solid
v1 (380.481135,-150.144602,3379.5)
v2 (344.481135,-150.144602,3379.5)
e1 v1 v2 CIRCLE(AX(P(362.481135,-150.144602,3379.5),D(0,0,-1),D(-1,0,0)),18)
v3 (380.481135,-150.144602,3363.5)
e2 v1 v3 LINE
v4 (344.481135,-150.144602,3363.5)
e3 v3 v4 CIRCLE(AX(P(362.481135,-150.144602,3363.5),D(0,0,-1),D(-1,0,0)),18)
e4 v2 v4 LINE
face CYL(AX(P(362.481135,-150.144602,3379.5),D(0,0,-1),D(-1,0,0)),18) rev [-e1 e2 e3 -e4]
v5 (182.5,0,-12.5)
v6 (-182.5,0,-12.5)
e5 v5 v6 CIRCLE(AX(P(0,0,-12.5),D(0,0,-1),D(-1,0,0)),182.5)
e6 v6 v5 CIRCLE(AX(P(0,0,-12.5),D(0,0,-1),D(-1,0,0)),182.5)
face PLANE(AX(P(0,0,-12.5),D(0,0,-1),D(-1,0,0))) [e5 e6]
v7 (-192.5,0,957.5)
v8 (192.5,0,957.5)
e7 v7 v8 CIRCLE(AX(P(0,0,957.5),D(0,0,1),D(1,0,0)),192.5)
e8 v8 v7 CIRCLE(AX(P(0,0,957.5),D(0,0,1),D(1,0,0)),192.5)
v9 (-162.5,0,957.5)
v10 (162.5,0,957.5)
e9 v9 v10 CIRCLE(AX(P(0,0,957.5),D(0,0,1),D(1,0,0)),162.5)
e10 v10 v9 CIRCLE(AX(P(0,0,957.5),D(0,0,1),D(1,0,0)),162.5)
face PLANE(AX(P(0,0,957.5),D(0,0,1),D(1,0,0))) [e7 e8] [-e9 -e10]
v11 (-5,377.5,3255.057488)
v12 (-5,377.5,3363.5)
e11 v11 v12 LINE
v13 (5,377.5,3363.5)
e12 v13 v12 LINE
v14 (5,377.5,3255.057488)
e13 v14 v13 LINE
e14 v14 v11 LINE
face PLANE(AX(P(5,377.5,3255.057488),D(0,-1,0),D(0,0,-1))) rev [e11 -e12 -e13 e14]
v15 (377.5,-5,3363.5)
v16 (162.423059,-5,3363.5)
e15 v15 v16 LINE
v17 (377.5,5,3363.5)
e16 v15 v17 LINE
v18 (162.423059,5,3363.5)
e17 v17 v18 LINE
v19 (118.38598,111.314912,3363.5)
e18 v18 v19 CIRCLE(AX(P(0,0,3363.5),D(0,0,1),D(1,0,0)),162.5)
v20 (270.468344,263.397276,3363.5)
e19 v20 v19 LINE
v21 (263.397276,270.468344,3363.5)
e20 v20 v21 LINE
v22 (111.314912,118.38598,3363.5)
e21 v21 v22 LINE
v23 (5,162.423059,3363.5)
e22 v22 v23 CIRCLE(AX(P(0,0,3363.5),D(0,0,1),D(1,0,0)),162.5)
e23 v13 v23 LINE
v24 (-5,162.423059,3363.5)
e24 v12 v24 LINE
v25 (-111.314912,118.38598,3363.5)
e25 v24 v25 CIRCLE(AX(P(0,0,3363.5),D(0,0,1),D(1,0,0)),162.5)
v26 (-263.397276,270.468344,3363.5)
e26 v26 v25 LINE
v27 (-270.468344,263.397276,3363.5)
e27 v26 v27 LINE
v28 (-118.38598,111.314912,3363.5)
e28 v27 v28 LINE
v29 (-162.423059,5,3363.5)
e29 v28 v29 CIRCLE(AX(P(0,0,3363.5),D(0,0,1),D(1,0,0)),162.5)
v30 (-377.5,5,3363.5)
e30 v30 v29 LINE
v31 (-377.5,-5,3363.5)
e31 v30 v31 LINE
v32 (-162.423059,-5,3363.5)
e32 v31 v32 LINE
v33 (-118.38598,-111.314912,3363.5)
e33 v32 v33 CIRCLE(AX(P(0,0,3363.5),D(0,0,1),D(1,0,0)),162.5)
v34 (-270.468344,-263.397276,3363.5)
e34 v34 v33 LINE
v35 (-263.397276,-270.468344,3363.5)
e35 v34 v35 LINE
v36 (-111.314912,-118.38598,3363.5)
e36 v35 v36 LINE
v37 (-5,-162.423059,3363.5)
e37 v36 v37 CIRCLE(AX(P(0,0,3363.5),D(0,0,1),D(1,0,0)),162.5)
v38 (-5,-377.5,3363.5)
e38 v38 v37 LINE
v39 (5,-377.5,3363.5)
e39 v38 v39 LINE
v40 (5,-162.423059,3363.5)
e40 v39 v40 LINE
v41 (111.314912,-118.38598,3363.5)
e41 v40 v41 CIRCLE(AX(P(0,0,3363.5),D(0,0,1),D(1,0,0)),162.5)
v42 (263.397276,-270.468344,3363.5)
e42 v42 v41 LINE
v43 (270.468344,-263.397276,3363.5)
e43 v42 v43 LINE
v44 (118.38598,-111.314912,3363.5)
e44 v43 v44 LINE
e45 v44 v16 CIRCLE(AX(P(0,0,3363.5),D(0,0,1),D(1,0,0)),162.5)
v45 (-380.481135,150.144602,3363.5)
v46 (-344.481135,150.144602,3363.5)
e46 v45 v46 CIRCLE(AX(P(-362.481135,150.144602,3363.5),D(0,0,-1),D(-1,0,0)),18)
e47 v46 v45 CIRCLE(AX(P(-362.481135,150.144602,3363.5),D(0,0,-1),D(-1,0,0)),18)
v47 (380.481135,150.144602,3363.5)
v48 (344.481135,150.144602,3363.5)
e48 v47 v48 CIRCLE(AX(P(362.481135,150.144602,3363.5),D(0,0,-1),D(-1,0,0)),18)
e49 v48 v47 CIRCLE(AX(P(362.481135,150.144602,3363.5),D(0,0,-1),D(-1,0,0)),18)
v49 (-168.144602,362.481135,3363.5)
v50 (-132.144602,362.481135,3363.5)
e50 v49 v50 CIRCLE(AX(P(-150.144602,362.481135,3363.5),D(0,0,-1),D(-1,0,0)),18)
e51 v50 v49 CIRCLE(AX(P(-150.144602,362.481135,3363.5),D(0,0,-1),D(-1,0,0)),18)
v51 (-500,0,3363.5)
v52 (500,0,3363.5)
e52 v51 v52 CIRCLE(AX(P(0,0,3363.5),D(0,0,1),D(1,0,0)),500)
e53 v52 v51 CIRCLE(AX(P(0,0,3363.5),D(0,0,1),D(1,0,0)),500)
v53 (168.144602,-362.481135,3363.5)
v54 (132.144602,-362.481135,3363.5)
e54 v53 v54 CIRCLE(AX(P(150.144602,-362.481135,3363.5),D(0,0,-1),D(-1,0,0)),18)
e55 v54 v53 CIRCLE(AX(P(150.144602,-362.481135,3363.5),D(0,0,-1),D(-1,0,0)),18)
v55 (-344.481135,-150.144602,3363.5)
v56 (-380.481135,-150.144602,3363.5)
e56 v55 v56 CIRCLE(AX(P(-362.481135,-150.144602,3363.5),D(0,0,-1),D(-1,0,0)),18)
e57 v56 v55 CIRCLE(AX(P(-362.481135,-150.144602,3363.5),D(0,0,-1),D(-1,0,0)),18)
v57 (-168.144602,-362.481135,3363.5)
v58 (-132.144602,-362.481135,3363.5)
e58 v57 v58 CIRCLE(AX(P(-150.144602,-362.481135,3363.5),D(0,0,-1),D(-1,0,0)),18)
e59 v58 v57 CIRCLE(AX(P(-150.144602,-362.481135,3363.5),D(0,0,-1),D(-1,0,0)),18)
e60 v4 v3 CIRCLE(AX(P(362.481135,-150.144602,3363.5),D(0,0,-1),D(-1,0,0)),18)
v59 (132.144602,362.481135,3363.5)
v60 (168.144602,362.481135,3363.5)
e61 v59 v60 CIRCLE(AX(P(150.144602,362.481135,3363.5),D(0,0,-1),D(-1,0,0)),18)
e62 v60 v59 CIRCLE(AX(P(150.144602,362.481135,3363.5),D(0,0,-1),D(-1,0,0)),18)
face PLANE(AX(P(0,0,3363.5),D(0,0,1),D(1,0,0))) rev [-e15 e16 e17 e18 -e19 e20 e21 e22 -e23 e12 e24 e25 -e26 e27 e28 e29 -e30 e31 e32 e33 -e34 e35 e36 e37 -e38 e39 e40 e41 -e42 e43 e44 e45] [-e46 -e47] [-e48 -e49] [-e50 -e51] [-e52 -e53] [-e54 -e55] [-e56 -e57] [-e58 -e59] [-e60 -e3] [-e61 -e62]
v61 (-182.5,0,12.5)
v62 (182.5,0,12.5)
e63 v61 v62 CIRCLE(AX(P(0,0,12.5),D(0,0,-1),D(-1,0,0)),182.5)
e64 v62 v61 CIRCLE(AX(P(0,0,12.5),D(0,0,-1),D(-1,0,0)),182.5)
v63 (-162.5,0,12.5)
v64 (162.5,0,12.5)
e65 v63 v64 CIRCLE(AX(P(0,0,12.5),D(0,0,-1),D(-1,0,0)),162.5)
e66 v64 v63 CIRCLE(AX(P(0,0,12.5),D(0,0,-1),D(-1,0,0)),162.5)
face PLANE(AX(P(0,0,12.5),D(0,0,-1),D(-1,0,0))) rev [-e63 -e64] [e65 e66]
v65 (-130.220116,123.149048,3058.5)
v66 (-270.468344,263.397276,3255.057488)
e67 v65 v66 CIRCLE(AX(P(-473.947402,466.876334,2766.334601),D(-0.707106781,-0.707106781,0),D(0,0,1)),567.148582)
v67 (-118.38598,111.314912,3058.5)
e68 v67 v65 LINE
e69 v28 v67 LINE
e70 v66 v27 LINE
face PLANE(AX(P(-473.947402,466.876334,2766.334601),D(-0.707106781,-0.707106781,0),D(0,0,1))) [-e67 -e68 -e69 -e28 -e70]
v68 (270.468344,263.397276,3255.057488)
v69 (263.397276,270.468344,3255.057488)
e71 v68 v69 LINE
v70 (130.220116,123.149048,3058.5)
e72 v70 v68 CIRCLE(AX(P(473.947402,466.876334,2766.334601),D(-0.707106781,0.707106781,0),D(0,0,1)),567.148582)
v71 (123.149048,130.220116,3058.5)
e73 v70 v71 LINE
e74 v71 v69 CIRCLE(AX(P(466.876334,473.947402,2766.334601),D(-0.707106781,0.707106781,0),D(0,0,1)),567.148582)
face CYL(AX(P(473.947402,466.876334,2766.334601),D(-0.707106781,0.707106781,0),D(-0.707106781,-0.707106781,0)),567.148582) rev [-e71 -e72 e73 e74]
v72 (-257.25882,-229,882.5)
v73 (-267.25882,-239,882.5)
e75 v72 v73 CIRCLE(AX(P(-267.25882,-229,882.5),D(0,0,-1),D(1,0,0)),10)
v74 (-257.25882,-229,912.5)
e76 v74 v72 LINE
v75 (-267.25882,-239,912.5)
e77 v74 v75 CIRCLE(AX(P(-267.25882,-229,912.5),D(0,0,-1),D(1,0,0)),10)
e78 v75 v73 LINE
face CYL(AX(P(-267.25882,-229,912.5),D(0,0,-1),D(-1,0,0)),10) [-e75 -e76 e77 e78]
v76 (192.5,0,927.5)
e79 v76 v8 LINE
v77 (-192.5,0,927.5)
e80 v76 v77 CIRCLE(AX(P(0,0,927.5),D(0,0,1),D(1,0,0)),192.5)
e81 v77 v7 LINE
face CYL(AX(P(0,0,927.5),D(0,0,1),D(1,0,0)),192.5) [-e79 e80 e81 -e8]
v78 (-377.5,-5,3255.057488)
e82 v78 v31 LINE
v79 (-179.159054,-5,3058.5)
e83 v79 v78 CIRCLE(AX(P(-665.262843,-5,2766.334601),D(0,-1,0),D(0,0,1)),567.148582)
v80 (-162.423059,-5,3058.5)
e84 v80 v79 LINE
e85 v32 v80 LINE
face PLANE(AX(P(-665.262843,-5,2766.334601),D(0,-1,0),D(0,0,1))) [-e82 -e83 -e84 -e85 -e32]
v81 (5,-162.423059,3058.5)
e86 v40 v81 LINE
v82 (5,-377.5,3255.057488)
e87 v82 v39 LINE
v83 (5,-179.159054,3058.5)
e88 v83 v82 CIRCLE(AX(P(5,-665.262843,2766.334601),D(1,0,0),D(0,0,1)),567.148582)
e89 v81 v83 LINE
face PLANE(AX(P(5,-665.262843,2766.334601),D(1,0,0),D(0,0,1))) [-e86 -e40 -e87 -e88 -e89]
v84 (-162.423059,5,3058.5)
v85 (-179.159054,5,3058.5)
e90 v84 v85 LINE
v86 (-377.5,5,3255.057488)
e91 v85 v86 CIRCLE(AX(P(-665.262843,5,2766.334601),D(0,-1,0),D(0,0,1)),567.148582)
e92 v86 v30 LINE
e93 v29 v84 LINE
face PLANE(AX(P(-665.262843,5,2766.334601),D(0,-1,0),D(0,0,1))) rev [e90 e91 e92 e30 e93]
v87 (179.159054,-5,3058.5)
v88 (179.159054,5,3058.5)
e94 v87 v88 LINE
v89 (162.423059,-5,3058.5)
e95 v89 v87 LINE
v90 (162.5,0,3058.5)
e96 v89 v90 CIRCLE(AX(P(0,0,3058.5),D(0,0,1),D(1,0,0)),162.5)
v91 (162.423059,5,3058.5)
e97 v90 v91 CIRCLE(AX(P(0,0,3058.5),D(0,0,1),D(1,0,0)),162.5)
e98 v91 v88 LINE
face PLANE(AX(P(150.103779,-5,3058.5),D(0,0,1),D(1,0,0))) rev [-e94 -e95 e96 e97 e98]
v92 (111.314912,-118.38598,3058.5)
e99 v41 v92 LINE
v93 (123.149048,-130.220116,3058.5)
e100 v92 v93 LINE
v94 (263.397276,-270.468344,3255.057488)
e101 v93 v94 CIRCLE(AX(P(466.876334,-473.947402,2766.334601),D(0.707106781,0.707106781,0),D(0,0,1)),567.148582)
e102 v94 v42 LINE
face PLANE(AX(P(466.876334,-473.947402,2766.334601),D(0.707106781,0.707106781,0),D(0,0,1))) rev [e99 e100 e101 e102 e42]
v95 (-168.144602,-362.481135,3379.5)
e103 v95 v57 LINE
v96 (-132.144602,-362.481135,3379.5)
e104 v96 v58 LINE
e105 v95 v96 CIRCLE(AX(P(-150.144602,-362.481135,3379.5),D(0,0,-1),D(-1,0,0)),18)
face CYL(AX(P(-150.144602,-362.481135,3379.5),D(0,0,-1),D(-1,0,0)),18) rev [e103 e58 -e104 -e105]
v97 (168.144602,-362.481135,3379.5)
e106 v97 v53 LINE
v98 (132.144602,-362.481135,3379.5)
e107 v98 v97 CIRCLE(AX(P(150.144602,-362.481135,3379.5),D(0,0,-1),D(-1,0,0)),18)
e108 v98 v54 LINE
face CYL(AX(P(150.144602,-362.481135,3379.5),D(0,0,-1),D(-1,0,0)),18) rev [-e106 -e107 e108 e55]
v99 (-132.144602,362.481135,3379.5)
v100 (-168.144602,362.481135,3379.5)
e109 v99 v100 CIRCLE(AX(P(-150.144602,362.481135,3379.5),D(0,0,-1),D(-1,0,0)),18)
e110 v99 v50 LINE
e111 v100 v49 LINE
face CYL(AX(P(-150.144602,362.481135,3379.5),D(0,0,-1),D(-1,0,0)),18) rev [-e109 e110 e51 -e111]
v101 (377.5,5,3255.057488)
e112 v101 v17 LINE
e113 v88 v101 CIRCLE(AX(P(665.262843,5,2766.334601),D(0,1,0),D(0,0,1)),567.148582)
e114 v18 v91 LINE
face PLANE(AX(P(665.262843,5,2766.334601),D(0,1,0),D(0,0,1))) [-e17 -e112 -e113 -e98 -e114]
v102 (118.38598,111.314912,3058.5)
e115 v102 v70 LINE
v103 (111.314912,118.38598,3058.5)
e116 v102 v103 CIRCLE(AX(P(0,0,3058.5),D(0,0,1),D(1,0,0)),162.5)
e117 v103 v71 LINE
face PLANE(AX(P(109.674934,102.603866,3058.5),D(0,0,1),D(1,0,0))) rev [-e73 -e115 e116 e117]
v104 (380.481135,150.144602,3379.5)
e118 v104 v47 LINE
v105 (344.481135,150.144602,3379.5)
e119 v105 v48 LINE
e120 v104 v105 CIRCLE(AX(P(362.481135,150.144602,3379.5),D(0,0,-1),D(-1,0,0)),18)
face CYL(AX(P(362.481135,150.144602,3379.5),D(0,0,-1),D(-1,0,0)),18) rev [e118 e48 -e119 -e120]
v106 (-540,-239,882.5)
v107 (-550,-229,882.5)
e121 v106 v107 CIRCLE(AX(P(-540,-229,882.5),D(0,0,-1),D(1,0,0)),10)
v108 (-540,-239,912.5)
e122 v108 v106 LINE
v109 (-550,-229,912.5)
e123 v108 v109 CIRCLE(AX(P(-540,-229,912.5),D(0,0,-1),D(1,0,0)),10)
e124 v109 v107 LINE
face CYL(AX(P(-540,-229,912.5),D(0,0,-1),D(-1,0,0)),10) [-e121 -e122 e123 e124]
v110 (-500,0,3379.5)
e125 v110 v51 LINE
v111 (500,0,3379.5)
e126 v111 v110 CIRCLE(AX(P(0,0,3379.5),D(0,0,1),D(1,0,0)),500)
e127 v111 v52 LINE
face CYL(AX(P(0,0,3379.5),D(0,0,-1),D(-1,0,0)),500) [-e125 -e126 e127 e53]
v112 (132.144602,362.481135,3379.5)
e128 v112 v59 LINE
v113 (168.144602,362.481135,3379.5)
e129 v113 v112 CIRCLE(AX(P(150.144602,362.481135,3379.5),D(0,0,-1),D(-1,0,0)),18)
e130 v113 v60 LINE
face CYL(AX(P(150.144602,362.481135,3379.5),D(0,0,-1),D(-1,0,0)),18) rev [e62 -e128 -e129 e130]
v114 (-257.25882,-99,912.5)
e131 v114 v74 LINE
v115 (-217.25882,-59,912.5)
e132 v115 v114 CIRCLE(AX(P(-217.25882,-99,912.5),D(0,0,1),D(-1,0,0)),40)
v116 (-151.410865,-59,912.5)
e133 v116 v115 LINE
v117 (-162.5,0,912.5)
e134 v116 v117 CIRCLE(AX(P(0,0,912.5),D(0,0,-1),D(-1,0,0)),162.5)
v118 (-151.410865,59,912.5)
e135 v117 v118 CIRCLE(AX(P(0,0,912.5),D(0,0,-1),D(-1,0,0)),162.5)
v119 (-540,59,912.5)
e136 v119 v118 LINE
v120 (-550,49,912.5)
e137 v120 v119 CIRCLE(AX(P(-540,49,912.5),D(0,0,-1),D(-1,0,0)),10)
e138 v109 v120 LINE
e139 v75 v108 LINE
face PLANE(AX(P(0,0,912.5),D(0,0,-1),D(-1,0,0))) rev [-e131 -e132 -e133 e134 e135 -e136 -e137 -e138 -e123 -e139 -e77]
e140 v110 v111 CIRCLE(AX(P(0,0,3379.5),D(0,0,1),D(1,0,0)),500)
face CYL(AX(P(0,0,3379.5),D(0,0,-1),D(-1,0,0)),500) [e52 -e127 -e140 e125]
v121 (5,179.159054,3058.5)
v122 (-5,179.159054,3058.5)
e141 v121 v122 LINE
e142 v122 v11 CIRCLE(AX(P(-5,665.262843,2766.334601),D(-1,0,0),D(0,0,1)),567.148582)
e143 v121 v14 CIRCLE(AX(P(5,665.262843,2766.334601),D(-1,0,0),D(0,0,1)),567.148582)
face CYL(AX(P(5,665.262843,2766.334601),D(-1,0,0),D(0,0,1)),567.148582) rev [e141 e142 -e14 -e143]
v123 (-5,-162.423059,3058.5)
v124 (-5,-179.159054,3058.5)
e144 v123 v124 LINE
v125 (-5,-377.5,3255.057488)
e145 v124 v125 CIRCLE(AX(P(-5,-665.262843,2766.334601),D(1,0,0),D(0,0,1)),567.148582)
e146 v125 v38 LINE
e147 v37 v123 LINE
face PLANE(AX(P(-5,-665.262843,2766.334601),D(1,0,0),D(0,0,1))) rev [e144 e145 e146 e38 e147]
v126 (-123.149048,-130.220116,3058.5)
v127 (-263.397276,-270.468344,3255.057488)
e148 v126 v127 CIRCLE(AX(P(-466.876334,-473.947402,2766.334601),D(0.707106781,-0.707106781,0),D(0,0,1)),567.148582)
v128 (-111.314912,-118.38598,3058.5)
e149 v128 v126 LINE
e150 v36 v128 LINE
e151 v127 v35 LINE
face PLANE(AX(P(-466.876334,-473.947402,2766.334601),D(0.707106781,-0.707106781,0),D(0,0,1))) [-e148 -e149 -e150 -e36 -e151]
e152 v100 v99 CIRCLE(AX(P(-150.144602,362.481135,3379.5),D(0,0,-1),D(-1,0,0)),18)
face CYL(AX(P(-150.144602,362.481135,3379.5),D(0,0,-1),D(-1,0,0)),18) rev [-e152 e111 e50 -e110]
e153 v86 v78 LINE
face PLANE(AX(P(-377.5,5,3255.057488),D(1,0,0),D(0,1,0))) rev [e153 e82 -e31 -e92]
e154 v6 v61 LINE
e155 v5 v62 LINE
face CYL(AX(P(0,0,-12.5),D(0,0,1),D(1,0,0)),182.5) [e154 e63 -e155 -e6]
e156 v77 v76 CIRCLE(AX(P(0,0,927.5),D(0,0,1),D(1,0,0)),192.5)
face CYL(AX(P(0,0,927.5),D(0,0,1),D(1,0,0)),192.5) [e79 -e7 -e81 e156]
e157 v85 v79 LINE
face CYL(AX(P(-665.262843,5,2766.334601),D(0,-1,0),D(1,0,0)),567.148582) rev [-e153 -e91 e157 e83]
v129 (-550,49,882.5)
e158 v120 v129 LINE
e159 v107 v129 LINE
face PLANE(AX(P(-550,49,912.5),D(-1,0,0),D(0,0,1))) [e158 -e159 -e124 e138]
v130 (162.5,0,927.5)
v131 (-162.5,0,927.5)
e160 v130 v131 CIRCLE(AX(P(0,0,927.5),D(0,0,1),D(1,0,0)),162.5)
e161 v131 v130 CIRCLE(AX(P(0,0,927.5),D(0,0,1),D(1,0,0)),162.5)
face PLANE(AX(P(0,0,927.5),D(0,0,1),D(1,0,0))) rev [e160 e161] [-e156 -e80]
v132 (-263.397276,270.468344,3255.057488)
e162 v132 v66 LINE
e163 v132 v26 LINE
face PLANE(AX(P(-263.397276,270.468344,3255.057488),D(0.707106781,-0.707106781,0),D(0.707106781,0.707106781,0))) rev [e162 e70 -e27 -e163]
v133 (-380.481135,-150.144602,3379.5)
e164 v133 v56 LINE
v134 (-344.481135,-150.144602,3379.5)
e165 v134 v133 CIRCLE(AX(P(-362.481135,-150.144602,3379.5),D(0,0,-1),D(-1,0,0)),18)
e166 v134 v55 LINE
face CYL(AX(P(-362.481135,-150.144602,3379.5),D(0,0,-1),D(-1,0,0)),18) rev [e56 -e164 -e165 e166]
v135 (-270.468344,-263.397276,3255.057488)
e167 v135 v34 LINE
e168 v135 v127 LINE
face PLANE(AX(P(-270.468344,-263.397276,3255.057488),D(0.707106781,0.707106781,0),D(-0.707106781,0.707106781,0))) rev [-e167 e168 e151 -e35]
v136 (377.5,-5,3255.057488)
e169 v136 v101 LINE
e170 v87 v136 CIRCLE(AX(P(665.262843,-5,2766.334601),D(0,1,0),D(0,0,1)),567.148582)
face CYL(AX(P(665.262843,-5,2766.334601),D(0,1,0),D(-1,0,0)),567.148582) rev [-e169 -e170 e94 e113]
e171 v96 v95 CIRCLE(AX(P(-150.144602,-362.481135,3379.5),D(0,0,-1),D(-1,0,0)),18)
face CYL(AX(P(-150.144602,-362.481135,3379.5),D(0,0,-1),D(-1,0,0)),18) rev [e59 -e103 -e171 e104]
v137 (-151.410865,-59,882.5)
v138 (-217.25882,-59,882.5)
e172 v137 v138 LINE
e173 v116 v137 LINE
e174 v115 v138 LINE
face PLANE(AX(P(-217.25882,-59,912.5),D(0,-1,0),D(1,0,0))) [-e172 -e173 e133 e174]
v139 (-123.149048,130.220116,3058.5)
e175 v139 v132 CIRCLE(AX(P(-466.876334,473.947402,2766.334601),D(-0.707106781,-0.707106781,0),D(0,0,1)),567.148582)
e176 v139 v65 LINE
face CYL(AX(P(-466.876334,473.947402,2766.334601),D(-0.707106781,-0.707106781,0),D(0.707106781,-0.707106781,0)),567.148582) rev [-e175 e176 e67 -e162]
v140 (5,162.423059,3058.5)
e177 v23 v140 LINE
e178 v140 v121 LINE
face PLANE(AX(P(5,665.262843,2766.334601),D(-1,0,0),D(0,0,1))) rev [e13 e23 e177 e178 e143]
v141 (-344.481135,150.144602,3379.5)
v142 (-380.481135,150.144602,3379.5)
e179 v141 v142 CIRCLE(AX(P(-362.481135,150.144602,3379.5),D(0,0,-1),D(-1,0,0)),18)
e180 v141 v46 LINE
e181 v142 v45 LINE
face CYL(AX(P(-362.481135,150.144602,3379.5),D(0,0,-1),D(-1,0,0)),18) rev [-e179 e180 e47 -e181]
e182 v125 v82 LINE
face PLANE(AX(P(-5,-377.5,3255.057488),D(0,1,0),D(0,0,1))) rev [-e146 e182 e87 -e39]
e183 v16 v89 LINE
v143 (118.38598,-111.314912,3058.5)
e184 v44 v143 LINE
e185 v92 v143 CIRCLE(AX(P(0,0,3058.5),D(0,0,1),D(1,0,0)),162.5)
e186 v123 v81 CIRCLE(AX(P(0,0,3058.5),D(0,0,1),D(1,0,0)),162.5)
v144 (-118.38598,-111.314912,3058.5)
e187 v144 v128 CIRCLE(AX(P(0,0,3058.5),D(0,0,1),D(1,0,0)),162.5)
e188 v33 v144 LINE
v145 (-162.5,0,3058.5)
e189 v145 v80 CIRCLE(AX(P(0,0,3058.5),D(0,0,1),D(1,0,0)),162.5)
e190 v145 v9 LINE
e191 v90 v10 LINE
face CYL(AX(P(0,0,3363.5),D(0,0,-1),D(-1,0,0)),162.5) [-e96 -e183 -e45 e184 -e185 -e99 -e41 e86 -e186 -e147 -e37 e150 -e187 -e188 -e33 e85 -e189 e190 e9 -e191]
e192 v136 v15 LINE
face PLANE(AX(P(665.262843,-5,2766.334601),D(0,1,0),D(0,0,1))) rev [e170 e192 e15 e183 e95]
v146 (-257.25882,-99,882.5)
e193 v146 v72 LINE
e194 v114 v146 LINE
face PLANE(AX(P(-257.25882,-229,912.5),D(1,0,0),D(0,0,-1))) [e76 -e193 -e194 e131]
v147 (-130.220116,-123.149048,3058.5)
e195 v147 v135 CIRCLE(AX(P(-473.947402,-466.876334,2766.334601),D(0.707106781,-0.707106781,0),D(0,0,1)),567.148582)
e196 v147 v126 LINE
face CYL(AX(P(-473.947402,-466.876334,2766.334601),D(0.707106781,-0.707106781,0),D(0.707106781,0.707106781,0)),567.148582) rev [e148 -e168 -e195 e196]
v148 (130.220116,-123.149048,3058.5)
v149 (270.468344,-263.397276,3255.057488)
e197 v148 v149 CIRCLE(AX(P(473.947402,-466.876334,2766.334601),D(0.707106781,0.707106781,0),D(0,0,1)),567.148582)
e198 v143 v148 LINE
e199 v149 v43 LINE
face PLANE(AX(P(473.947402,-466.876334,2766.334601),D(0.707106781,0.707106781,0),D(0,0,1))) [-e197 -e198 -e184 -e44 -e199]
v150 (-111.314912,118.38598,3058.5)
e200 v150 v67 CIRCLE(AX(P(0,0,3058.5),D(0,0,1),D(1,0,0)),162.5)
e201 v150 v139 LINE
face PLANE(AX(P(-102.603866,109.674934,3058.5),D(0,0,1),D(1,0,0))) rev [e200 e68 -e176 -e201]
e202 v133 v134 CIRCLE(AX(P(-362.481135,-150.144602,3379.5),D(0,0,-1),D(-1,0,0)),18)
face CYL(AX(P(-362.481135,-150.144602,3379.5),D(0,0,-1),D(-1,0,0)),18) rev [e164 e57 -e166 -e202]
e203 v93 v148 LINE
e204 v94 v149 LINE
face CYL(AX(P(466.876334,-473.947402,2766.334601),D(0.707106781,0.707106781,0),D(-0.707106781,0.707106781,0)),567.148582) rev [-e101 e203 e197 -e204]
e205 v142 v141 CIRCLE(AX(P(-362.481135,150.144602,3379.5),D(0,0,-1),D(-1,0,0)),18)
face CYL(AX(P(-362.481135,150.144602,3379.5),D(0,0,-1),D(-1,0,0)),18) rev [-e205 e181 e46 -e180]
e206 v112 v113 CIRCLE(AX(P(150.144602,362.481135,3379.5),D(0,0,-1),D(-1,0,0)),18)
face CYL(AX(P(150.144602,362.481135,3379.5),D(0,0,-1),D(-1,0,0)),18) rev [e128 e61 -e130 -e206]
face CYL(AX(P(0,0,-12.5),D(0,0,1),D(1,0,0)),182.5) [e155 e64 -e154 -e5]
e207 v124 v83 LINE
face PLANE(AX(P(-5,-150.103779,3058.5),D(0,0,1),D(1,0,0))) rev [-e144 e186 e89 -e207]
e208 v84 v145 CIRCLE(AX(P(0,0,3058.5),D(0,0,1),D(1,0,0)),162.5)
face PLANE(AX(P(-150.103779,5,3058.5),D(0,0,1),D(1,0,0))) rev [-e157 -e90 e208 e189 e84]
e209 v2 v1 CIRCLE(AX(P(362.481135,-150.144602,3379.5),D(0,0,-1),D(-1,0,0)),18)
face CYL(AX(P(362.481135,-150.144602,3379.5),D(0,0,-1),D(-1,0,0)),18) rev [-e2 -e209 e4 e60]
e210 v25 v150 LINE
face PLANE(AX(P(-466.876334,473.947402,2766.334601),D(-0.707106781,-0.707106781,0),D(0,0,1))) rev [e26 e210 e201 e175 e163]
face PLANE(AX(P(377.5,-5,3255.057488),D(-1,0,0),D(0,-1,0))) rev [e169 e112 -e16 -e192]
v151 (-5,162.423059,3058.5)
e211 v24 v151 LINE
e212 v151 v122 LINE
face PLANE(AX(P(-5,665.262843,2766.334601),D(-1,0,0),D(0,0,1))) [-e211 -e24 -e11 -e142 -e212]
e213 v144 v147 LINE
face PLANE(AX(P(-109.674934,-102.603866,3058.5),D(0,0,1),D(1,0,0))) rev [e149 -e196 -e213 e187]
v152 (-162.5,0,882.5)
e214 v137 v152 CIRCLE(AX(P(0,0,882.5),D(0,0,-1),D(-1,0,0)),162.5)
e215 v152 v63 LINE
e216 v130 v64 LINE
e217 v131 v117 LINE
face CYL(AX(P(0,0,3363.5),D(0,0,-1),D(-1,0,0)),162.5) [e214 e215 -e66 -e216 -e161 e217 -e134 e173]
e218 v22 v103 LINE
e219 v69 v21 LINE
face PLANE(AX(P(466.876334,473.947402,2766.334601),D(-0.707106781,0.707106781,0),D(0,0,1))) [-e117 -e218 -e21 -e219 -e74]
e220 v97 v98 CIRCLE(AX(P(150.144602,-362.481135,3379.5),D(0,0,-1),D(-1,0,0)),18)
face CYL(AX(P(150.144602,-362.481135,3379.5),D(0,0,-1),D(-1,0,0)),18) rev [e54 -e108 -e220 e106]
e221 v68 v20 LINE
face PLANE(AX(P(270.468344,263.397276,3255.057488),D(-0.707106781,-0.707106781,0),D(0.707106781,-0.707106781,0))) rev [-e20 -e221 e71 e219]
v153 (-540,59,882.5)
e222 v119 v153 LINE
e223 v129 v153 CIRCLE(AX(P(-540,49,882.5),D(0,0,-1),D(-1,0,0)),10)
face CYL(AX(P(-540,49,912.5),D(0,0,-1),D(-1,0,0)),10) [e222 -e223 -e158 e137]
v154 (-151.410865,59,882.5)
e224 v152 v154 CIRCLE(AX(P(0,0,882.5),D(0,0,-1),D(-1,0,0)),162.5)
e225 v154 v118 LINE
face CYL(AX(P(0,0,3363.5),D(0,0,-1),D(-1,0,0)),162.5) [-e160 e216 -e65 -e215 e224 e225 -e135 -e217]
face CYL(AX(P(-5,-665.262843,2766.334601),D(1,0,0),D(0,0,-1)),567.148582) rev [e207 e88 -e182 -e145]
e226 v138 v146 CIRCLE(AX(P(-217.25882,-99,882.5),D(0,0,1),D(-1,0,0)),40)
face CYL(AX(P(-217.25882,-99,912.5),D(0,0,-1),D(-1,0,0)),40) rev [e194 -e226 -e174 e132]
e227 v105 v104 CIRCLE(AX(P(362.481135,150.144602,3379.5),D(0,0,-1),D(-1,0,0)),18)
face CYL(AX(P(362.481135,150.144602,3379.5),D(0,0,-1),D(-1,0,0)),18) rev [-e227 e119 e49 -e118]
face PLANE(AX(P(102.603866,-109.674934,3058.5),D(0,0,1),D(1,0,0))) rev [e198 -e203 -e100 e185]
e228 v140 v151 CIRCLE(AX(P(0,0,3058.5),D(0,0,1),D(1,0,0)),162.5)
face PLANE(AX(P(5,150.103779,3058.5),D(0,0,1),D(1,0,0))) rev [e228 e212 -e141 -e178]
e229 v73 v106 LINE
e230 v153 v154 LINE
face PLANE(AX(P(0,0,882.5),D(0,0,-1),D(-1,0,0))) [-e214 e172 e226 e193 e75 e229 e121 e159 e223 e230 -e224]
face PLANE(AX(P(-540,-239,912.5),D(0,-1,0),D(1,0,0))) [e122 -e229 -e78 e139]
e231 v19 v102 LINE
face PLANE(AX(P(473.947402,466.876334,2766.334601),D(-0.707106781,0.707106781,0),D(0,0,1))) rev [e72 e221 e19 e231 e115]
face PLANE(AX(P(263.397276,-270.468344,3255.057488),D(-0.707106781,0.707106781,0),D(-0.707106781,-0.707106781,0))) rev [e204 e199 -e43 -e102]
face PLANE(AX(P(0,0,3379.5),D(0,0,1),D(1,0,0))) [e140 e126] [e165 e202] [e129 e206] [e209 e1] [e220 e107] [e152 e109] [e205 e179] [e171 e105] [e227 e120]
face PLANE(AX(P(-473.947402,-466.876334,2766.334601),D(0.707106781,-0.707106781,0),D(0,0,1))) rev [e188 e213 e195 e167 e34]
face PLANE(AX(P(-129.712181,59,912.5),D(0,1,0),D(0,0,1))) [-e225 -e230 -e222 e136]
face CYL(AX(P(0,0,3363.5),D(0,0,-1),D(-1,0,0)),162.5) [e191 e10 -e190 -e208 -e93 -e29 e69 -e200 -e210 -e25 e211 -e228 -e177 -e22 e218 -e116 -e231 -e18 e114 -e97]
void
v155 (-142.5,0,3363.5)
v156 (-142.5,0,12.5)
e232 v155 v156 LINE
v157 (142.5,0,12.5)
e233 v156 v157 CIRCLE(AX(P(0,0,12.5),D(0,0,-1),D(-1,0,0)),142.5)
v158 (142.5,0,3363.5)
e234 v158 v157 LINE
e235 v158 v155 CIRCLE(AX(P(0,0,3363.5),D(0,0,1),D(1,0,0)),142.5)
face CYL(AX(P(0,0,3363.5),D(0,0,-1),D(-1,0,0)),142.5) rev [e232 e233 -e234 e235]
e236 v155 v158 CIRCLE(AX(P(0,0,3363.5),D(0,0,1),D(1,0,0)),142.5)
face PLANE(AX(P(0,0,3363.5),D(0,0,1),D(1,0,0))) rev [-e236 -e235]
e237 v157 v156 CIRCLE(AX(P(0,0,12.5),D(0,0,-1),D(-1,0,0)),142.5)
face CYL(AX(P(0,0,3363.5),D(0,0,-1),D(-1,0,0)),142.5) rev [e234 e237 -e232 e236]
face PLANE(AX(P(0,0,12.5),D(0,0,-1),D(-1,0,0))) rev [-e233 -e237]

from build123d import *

# Parameters (mm, degrees)
SKETCH1_R           = 162.5
SKETCH1_R_2         = 142.5
BOSS_EXTRUDE1_DEPTH = 3363.5
BOSS_EXTRUDE2_START = -2436
SKETCH2_R           = 192.5
SKETCH2_R_2         = 162.5
BOSS_EXTRUDE2_DEPTH = 30
SKETCH3_R           = 500
BOSS_EXTRUDE3_DEPTH = 16
BOSS_EXTRUDE4_DEPTH = 5
CIRPATTERN1_COUNT   = 8
SKETCH5_R           = 18
CUT_EXTRUDE1_DEPTH  = 3438.023749
SKETCH6_R           = 182.5
BOSS_EXTRUDE5_DEPTH = 12.5
BOSS_EXTRUDE6_START = -895
BOSS_EXTRUDE6_DEPTH = 30


with BuildPart() as part:
    # Sketch1 → Boss-Extrude1 (new body)
    with BuildSketch(Plane.XY):
        Circle(SKETCH1_R)
        Circle(SKETCH1_R_2, mode=Mode.SUBTRACT)
    extrude(amount=BOSS_EXTRUDE1_DEPTH)

    # Sketch2 → Boss-Extrude2 (add)
    with BuildSketch(Plane.XY.offset(3363.5).offset(BOSS_EXTRUDE2_START)):
        Circle(SKETCH2_R)
        Circle(SKETCH2_R_2, mode=Mode.SUBTRACT)
    extrude(amount=BOSS_EXTRUDE2_DEPTH)

    # Sketch3 → Boss-Extrude3 (add)
    with BuildSketch(Plane.XY.offset(3363.5)):
        Circle(SKETCH3_R)
    extrude(amount=BOSS_EXTRUDE3_DEPTH)

    # Sketch4 → Boss-Extrude4 (add, symmetric)
    with BuildSketch(Plane(origin=(0, 0, 0), x_dir=(0, 0, -1), z_dir=(1, 0, 0))):
        with BuildLine():
            Line((-3058.5, 150.103779), (-3058.5, 179.159054))
            ThreePointArc((-3058.5, 179.159054), (-3169.176272, 266.043477), (-3255.057488, 377.5))
            Line((-3255.057488, 377.5), (-3363.5, 377.5))
            Line((-3363.5, 377.5), (-3363.5, 150.103779))
            Line((-3363.5, 150.103779), (-3058.5, 150.103779))
        make_face()
    boss_extrude4 = extrude(amount=BOSS_EXTRUDE4_DEPTH, both=True)

    # CirPattern1: Boss-Extrude4 ×8 about axis
    cirpattern1_axis = Axis((0, 0, 0), (0, 0, 1))
    for i in range(1, CIRPATTERN1_COUNT):
        add(boss_extrude4.rotate(cirpattern1_axis, i * 360 / CIRPATTERN1_COUNT))

    # Sketch5 → Cut-Extrude1 (cut, through all)
    with BuildSketch(Plane(origin=(0, 0, 3363.5), x_dir=(-1, 0, 0), z_dir=(0, 0, -1))):
        with Locations((150.144602, 362.481135)):
            Circle(SKETCH5_R)
        with Locations((362.481135, 150.144602)):
            Circle(SKETCH5_R)
        with Locations((362.481135, -150.144602)):
            Circle(SKETCH5_R)
        with Locations((150.144602, -362.481135)):
            Circle(SKETCH5_R)
        with Locations((-150.144602, -362.481135)):
            Circle(SKETCH5_R)
        with Locations((-362.481135, -150.144602)):
            Circle(SKETCH5_R)
        with Locations((-362.481135, 150.144602)):
            Circle(SKETCH5_R)
        with Locations((-150.144602, 362.481135)):
            Circle(SKETCH5_R)
    extrude(amount=-CUT_EXTRUDE1_DEPTH, mode=Mode.SUBTRACT)

    # Sketch6 → Boss-Extrude5 (add, symmetric)
    with BuildSketch(Plane(origin=(0, 0, 0), x_dir=(-1, 0, 0), z_dir=(0, 0, -1))):
        Circle(SKETCH6_R)
    extrude(amount=BOSS_EXTRUDE5_DEPTH, both=True)

    # Sketch7 → Boss-Extrude6 (add)
    with BuildSketch(Plane(origin=(0, 0, -12.5), x_dir=(-1, 0, 0), z_dir=(0, 0, -1)).offset(BOSS_EXTRUDE6_START)):
        with BuildLine():
            Line((129.712181, 59), (540, 59))
            ThreePointArc((540, 59), (547.071068, 56.071068), (550, 49))
            Line((550, 49), (550, 0))
            Line((550, 0), (550, -229))
            ThreePointArc((550, -229), (547.071068, -236.071068), (540, -239))
            Line((540, -239), (267.25882, -239))
            ThreePointArc((267.25882, -239), (260.187752, -236.071068), (257.25882, -229))
            Line((257.25882, -229), (257.25882, -99))
            ThreePointArc((257.25882, -99), (245.543091, -70.715729), (217.25882, -59))
            Line((217.25882, -59), (129.712181, -59))
            ThreePointArc((129.712181, -59), (142.5, 0), (129.712181, 59))
        make_face()
    extrude(amount=-BOSS_EXTRUDE6_DEPTH)


solid = part.part
